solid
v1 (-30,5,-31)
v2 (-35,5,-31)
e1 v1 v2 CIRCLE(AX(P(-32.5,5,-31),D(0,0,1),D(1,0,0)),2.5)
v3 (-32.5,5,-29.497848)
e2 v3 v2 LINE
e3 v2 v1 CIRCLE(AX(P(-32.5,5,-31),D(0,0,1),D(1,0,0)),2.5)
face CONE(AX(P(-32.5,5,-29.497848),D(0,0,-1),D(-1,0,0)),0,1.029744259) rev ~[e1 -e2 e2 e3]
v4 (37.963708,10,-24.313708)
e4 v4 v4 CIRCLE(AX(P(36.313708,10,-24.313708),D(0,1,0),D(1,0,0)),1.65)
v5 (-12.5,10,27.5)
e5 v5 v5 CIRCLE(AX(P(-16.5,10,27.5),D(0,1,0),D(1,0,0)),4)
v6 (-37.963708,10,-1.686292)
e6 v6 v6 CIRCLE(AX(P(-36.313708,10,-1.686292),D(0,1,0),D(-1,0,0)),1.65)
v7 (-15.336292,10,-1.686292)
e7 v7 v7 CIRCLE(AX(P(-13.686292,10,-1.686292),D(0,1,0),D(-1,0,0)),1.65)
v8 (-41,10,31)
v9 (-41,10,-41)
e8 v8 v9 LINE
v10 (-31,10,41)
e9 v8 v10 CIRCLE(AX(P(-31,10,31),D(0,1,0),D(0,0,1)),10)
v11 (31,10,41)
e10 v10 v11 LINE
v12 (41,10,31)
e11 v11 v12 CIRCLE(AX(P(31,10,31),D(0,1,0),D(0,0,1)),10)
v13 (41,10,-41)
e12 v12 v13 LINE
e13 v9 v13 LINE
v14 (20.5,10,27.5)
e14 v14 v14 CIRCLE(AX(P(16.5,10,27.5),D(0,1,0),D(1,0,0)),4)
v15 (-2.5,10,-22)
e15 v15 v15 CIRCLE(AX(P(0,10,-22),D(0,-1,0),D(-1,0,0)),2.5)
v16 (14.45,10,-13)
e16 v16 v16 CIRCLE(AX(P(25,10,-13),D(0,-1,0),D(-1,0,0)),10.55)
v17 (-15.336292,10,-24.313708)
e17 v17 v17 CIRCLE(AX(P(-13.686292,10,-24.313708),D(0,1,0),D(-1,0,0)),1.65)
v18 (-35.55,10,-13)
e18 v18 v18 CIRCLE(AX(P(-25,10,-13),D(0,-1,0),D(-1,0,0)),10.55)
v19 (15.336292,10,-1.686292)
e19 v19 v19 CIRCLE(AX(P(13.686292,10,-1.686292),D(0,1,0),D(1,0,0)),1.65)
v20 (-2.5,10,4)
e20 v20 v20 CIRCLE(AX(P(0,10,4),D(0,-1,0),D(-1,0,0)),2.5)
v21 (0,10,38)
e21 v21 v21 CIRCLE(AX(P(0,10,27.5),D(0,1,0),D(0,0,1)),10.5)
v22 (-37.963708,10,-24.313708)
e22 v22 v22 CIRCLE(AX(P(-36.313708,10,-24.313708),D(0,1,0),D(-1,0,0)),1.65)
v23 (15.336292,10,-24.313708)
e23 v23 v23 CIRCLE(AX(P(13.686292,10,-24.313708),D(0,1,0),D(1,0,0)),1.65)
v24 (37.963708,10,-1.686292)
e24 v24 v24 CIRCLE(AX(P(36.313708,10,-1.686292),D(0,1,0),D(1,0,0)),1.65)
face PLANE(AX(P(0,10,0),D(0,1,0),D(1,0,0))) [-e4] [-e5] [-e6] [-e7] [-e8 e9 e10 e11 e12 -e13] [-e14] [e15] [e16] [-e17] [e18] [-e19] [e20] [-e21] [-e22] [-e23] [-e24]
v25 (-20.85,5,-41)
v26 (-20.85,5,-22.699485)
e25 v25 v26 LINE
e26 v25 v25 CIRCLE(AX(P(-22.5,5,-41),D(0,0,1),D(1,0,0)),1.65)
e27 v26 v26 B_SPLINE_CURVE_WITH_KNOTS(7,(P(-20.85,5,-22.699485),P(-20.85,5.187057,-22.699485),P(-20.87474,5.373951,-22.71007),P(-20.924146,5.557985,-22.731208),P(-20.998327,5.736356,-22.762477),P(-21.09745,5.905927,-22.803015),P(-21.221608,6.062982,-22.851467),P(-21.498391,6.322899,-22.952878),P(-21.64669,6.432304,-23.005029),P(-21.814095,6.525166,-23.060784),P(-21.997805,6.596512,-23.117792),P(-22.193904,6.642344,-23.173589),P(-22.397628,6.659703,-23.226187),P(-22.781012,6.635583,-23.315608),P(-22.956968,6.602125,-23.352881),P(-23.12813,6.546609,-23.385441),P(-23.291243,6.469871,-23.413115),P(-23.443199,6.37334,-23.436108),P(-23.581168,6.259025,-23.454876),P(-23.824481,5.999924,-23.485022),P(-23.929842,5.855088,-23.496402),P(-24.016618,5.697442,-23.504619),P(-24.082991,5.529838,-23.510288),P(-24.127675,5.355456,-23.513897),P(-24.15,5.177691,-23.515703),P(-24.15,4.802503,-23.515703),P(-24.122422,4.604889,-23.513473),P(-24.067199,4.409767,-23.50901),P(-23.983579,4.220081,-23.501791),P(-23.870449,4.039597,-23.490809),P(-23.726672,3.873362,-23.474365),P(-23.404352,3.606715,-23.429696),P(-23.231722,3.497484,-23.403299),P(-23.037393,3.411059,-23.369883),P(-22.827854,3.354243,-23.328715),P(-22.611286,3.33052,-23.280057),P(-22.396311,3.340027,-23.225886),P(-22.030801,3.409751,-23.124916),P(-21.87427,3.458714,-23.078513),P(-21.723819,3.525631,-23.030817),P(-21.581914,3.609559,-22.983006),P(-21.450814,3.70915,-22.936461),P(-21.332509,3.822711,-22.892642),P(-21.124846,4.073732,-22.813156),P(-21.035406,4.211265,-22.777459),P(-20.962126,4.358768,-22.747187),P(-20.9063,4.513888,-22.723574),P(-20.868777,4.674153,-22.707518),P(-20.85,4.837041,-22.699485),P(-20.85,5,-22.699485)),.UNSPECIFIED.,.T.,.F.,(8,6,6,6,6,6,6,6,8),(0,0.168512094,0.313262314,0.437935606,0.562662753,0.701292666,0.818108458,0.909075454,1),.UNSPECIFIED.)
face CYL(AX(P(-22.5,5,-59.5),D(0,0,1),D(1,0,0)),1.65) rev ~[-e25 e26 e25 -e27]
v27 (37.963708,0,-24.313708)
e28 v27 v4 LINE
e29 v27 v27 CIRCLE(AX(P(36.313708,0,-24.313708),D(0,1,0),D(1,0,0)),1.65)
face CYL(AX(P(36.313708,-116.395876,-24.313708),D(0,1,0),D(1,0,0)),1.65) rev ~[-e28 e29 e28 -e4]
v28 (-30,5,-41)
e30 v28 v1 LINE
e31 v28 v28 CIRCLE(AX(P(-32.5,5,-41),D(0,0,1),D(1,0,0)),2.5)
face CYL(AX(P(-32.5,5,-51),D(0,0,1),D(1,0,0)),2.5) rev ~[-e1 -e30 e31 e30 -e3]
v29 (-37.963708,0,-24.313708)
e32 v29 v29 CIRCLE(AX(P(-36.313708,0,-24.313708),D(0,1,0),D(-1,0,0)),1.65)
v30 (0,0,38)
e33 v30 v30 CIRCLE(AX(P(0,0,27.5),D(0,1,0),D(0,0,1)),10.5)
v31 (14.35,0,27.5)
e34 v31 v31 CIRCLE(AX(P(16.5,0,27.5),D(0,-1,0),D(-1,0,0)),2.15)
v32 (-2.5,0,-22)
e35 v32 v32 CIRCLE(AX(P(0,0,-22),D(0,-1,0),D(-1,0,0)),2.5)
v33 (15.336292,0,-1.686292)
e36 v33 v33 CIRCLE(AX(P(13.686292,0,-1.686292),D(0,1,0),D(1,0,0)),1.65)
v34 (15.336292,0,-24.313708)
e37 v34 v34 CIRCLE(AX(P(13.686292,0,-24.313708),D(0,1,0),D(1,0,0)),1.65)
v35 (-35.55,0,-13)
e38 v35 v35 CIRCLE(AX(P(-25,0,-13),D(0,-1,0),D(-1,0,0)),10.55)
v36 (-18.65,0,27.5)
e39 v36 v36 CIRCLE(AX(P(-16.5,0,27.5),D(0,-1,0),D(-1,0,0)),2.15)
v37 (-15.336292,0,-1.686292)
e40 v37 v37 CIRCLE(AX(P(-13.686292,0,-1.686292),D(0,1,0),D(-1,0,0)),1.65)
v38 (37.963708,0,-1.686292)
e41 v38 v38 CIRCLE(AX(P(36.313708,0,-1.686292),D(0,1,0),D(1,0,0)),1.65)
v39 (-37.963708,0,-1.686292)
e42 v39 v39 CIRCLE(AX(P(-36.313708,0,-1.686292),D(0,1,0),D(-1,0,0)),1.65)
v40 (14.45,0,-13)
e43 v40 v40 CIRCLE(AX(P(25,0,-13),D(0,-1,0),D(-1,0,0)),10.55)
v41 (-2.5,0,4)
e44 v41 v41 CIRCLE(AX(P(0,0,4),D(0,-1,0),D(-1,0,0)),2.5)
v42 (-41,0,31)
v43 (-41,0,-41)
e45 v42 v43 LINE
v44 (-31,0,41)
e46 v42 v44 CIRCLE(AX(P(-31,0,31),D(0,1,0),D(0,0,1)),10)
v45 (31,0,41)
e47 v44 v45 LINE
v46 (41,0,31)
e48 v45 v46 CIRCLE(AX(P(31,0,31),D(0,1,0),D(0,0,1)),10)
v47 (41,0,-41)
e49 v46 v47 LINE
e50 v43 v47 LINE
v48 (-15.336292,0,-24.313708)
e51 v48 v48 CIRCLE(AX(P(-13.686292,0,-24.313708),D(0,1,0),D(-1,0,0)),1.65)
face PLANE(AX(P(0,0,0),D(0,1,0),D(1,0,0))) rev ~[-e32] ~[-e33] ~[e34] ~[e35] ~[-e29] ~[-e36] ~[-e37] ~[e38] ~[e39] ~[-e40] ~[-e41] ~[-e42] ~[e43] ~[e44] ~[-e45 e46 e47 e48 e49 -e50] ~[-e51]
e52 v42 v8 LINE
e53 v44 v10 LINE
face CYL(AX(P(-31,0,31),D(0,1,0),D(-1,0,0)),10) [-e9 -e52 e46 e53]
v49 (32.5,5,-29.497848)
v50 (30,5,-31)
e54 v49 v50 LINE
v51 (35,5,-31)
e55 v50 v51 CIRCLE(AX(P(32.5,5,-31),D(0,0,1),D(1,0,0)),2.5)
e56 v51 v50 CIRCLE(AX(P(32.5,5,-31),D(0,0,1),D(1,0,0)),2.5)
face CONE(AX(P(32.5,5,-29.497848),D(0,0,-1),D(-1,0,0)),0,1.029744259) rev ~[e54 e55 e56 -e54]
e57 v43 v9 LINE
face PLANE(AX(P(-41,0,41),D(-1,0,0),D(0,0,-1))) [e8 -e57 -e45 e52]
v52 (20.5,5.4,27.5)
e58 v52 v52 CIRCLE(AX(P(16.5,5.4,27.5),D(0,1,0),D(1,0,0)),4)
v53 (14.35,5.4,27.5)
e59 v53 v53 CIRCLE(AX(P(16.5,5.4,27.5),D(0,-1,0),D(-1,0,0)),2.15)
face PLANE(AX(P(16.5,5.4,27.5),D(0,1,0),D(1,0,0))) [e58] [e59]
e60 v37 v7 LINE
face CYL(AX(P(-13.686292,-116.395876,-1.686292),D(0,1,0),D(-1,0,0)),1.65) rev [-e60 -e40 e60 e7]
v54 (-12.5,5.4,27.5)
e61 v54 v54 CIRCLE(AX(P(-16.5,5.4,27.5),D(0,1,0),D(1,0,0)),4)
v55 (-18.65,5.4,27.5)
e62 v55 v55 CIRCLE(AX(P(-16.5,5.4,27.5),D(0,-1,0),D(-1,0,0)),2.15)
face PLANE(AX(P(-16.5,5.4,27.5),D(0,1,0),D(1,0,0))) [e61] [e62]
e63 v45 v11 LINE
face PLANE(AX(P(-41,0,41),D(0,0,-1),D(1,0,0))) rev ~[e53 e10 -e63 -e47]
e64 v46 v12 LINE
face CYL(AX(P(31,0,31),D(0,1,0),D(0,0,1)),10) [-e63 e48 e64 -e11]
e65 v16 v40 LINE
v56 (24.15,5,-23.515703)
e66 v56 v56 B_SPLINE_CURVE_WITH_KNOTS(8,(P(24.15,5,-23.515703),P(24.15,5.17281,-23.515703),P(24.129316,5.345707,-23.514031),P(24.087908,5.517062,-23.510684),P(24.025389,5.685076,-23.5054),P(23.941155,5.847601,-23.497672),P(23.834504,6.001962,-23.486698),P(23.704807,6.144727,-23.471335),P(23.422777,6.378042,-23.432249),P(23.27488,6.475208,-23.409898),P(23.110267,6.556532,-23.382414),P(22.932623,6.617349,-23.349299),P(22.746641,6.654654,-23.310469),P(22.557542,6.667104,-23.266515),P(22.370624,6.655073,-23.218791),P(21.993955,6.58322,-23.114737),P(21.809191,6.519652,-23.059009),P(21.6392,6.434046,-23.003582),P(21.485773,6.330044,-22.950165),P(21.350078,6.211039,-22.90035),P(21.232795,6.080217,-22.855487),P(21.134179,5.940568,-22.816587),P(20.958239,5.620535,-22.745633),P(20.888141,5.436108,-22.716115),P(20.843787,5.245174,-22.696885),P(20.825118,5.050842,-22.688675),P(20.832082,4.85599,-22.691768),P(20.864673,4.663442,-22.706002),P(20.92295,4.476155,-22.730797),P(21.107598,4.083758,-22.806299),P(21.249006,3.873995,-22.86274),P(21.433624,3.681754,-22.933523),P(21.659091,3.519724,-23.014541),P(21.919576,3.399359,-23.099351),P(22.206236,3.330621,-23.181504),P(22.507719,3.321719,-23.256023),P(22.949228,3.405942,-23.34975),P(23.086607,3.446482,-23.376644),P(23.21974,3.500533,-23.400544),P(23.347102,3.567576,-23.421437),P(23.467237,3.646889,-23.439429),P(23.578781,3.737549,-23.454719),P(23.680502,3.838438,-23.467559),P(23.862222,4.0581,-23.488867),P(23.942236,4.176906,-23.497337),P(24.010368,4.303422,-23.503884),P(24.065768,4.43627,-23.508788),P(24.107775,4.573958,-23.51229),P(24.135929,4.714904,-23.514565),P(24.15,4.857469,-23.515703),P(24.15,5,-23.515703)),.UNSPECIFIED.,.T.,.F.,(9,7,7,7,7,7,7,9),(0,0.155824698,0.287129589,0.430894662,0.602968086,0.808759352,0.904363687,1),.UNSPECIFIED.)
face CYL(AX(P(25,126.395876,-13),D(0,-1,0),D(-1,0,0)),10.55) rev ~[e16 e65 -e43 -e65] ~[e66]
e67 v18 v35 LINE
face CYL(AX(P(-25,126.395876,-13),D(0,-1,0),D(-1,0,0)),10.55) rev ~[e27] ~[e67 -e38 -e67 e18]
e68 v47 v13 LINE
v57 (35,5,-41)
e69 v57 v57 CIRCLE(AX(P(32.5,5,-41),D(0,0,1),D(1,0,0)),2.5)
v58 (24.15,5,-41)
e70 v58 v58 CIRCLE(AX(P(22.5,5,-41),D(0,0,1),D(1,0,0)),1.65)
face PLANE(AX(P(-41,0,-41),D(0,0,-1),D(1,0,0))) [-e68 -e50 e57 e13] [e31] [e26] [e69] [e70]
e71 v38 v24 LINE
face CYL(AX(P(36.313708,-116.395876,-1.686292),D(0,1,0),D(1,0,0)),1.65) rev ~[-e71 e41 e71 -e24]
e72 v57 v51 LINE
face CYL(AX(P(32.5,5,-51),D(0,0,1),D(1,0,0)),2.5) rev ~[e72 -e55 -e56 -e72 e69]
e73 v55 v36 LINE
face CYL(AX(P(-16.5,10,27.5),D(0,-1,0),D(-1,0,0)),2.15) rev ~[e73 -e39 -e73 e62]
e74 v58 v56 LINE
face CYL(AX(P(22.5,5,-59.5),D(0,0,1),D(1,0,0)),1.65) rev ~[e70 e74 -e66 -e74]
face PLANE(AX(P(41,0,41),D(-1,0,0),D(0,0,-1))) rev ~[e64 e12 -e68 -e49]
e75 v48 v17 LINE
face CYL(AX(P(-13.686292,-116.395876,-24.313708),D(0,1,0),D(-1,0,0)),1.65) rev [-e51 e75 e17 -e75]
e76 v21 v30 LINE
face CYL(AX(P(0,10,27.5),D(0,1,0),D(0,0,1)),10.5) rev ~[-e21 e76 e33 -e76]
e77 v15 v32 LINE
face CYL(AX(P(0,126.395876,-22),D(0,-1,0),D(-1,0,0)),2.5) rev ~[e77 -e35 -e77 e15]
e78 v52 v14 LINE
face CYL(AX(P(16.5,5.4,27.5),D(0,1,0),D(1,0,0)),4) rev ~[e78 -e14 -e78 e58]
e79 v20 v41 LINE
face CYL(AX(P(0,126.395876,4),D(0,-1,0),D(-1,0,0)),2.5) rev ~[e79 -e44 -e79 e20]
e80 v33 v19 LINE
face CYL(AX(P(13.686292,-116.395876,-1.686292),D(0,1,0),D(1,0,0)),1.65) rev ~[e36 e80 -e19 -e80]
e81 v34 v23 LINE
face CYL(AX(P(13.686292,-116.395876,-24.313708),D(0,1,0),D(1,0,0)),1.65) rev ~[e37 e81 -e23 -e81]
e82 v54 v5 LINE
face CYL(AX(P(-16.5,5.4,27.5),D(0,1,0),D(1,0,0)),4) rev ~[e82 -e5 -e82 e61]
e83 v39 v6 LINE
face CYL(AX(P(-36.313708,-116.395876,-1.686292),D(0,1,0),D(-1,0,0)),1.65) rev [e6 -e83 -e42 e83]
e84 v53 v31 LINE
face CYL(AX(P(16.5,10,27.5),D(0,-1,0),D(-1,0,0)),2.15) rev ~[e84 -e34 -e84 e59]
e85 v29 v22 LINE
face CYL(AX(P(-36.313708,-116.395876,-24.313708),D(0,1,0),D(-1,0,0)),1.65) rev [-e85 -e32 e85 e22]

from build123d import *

# Parameters (mm, degrees)
SKETCH_1_W                = 82
SKETCH_1_H                = 82
EXTRUDE_1_DEPTH           = 10
SKETCH_4_R                = 10.5
CUT_EXTRUDE_3_DEPTH       = 59.838762733
FILLET_9_R                = 10
HOLE_WIZARD_2_D           = 4.3
HOLE_WIZARD_2_CBORE_D     = 8
HOLE_WIZARD_2_CBORE_DEPTH = 4.6
HOLE_WIZARD_M4_2_D        = 3.3
HOLE_WIZARD_M4_2_DEPTH    = 18.5
HOLE_WIZARD_M4_2_TIP      = 0.991420021
MM_2_D                    = 21.1
HOLE_WIZARD_M4_3_D        = 3.3
HOLE_WIZARD_M6_1_D        = 5
HOLE_WIZARD_M6_2_D        = 5
HOLE_WIZARD_5_0_5_1_D     = 5
HOLE_WIZARD_5_0_5_1_DEPTH = 10
HOLE_WIZARD_5_0_5_1_TIP   = 1.502151548


with BuildPart() as part:
    # 草图1 → 凸台-拉伸1 (new body)
    with BuildSketch(Plane(origin=(0, 0, 0), x_dir=(1, 0, 0), z_dir=(0, 1, 0))):
        Rectangle(SKETCH_1_W, SKETCH_1_H)
    extrude(amount=EXTRUDE_1_DEPTH)

    # 草图4 → 切除-拉伸3 (cut, through all)
    with BuildSketch(Plane(origin=(0, 10, 0), x_dir=(1, 0, 0), z_dir=(0, 1, 0))):
        with Locations(Location((0, -27.5, 0), (0, 0, 270))):
            Circle(SKETCH_4_R)
    extrude(amount=-CUT_EXTRUDE_3_DEPTH, mode=Mode.SUBTRACT)

    # 圆角9
    fillet_9_edges = [part.edges().sort_by_distance(p)[0] for p in [
        (41, 5, 41),
        (-41, 5, 41),
    ]]
    fillet(fillet_9_edges, radius=FILLET_9_R)

    # 打孔尺寸(%根据)开槽圆柱头螺钉的类型2 (through all)
    with Locations(Plane(origin=(0, 10, 0), x_dir=(1, 0, 0), z_dir=(0, 1, 0))):
        with Locations((-16.5, -27.5), (16.5, -27.5)):
            CounterBoreHole(HOLE_WIZARD_2_D / 2, HOLE_WIZARD_2_CBORE_D / 2, HOLE_WIZARD_2_CBORE_DEPTH)

    # M4 螺纹孔2
    with Locations(Plane(origin=(0, 0, -41), x_dir=(-1, 0, 0), z_dir=(0, 0, -1))):
        with Locations((-22.5, 5), (22.5, 5)):
            Hole(HOLE_WIZARD_M4_2_D / 2, depth=HOLE_WIZARD_M4_2_DEPTH)
            with Locations((0, 0, -(HOLE_WIZARD_M4_2_DEPTH + HOLE_WIZARD_M4_2_TIP / 2))):  # 118° drill point
                Cone(0, HOLE_WIZARD_M4_2_D / 2, HOLE_WIZARD_M4_2_TIP, mode=Mode.SUBTRACT)

    # 大小mm 暗销孔2 (through all)
    with Locations(Plane(origin=(0, 10, 0), x_dir=(1, 0, 0), z_dir=(0, 1, 0))):
        with Locations((-25, 13), (25, 13)):
            Hole(MM_2_D / 2)

    # M4 螺纹孔3 (through all)
    with Locations(Plane(origin=(0, 0, 0), x_dir=(-1, 0, 0), z_dir=(0, -1, 0))):
        with Locations((-13.686291501, 24.313708499), (-13.686291501, 1.686291501), (-36.313708499, 1.686291501), (-36.313708499, 24.313708499)):
            hole_wizard_m4_3 = Hole(HOLE_WIZARD_M4_3_D / 2)

    # 镜向2: M4 螺纹孔3 across plane
    add(hole_wizard_m4_3.mirror(Plane(origin=(0, 0, 0), x_dir=(0, 0, 1), z_dir=(1, 0, 0))), mode=Mode.SUBTRACT)

    # M6 螺纹孔1 (through all)
    with Locations(Plane(origin=(0, 10, 0), x_dir=(1, 0, 0), z_dir=(0, 1, 0))):
        with Locations((0, 22)):
            Hole(HOLE_WIZARD_M6_1_D / 2)

    # M6 螺纹孔2 (through all)
    with Locations(Plane(origin=(0, 10, 0), x_dir=(1, 0, 0), z_dir=(0, 1, 0))):
        with Locations((0, -4)):
            Hole(HOLE_WIZARD_M6_2_D / 2)

    # Ø5.0 (5) 直径孔1
    with Locations(Plane(origin=(0, 0, -41), x_dir=(-1, 0, 0), z_dir=(0, 0, -1))):
        with Locations((-32.5, 5), (32.5, 5)):
            Hole(HOLE_WIZARD_5_0_5_1_D / 2, depth=HOLE_WIZARD_5_0_5_1_DEPTH)
            with Locations((0, 0, -(HOLE_WIZARD_5_0_5_1_DEPTH + HOLE_WIZARD_5_0_5_1_TIP / 2))):  # 118° drill point
                Cone(0, HOLE_WIZARD_5_0_5_1_D / 2, HOLE_WIZARD_5_0_5_1_TIP, mode=Mode.SUBTRACT)


solid = part.part
